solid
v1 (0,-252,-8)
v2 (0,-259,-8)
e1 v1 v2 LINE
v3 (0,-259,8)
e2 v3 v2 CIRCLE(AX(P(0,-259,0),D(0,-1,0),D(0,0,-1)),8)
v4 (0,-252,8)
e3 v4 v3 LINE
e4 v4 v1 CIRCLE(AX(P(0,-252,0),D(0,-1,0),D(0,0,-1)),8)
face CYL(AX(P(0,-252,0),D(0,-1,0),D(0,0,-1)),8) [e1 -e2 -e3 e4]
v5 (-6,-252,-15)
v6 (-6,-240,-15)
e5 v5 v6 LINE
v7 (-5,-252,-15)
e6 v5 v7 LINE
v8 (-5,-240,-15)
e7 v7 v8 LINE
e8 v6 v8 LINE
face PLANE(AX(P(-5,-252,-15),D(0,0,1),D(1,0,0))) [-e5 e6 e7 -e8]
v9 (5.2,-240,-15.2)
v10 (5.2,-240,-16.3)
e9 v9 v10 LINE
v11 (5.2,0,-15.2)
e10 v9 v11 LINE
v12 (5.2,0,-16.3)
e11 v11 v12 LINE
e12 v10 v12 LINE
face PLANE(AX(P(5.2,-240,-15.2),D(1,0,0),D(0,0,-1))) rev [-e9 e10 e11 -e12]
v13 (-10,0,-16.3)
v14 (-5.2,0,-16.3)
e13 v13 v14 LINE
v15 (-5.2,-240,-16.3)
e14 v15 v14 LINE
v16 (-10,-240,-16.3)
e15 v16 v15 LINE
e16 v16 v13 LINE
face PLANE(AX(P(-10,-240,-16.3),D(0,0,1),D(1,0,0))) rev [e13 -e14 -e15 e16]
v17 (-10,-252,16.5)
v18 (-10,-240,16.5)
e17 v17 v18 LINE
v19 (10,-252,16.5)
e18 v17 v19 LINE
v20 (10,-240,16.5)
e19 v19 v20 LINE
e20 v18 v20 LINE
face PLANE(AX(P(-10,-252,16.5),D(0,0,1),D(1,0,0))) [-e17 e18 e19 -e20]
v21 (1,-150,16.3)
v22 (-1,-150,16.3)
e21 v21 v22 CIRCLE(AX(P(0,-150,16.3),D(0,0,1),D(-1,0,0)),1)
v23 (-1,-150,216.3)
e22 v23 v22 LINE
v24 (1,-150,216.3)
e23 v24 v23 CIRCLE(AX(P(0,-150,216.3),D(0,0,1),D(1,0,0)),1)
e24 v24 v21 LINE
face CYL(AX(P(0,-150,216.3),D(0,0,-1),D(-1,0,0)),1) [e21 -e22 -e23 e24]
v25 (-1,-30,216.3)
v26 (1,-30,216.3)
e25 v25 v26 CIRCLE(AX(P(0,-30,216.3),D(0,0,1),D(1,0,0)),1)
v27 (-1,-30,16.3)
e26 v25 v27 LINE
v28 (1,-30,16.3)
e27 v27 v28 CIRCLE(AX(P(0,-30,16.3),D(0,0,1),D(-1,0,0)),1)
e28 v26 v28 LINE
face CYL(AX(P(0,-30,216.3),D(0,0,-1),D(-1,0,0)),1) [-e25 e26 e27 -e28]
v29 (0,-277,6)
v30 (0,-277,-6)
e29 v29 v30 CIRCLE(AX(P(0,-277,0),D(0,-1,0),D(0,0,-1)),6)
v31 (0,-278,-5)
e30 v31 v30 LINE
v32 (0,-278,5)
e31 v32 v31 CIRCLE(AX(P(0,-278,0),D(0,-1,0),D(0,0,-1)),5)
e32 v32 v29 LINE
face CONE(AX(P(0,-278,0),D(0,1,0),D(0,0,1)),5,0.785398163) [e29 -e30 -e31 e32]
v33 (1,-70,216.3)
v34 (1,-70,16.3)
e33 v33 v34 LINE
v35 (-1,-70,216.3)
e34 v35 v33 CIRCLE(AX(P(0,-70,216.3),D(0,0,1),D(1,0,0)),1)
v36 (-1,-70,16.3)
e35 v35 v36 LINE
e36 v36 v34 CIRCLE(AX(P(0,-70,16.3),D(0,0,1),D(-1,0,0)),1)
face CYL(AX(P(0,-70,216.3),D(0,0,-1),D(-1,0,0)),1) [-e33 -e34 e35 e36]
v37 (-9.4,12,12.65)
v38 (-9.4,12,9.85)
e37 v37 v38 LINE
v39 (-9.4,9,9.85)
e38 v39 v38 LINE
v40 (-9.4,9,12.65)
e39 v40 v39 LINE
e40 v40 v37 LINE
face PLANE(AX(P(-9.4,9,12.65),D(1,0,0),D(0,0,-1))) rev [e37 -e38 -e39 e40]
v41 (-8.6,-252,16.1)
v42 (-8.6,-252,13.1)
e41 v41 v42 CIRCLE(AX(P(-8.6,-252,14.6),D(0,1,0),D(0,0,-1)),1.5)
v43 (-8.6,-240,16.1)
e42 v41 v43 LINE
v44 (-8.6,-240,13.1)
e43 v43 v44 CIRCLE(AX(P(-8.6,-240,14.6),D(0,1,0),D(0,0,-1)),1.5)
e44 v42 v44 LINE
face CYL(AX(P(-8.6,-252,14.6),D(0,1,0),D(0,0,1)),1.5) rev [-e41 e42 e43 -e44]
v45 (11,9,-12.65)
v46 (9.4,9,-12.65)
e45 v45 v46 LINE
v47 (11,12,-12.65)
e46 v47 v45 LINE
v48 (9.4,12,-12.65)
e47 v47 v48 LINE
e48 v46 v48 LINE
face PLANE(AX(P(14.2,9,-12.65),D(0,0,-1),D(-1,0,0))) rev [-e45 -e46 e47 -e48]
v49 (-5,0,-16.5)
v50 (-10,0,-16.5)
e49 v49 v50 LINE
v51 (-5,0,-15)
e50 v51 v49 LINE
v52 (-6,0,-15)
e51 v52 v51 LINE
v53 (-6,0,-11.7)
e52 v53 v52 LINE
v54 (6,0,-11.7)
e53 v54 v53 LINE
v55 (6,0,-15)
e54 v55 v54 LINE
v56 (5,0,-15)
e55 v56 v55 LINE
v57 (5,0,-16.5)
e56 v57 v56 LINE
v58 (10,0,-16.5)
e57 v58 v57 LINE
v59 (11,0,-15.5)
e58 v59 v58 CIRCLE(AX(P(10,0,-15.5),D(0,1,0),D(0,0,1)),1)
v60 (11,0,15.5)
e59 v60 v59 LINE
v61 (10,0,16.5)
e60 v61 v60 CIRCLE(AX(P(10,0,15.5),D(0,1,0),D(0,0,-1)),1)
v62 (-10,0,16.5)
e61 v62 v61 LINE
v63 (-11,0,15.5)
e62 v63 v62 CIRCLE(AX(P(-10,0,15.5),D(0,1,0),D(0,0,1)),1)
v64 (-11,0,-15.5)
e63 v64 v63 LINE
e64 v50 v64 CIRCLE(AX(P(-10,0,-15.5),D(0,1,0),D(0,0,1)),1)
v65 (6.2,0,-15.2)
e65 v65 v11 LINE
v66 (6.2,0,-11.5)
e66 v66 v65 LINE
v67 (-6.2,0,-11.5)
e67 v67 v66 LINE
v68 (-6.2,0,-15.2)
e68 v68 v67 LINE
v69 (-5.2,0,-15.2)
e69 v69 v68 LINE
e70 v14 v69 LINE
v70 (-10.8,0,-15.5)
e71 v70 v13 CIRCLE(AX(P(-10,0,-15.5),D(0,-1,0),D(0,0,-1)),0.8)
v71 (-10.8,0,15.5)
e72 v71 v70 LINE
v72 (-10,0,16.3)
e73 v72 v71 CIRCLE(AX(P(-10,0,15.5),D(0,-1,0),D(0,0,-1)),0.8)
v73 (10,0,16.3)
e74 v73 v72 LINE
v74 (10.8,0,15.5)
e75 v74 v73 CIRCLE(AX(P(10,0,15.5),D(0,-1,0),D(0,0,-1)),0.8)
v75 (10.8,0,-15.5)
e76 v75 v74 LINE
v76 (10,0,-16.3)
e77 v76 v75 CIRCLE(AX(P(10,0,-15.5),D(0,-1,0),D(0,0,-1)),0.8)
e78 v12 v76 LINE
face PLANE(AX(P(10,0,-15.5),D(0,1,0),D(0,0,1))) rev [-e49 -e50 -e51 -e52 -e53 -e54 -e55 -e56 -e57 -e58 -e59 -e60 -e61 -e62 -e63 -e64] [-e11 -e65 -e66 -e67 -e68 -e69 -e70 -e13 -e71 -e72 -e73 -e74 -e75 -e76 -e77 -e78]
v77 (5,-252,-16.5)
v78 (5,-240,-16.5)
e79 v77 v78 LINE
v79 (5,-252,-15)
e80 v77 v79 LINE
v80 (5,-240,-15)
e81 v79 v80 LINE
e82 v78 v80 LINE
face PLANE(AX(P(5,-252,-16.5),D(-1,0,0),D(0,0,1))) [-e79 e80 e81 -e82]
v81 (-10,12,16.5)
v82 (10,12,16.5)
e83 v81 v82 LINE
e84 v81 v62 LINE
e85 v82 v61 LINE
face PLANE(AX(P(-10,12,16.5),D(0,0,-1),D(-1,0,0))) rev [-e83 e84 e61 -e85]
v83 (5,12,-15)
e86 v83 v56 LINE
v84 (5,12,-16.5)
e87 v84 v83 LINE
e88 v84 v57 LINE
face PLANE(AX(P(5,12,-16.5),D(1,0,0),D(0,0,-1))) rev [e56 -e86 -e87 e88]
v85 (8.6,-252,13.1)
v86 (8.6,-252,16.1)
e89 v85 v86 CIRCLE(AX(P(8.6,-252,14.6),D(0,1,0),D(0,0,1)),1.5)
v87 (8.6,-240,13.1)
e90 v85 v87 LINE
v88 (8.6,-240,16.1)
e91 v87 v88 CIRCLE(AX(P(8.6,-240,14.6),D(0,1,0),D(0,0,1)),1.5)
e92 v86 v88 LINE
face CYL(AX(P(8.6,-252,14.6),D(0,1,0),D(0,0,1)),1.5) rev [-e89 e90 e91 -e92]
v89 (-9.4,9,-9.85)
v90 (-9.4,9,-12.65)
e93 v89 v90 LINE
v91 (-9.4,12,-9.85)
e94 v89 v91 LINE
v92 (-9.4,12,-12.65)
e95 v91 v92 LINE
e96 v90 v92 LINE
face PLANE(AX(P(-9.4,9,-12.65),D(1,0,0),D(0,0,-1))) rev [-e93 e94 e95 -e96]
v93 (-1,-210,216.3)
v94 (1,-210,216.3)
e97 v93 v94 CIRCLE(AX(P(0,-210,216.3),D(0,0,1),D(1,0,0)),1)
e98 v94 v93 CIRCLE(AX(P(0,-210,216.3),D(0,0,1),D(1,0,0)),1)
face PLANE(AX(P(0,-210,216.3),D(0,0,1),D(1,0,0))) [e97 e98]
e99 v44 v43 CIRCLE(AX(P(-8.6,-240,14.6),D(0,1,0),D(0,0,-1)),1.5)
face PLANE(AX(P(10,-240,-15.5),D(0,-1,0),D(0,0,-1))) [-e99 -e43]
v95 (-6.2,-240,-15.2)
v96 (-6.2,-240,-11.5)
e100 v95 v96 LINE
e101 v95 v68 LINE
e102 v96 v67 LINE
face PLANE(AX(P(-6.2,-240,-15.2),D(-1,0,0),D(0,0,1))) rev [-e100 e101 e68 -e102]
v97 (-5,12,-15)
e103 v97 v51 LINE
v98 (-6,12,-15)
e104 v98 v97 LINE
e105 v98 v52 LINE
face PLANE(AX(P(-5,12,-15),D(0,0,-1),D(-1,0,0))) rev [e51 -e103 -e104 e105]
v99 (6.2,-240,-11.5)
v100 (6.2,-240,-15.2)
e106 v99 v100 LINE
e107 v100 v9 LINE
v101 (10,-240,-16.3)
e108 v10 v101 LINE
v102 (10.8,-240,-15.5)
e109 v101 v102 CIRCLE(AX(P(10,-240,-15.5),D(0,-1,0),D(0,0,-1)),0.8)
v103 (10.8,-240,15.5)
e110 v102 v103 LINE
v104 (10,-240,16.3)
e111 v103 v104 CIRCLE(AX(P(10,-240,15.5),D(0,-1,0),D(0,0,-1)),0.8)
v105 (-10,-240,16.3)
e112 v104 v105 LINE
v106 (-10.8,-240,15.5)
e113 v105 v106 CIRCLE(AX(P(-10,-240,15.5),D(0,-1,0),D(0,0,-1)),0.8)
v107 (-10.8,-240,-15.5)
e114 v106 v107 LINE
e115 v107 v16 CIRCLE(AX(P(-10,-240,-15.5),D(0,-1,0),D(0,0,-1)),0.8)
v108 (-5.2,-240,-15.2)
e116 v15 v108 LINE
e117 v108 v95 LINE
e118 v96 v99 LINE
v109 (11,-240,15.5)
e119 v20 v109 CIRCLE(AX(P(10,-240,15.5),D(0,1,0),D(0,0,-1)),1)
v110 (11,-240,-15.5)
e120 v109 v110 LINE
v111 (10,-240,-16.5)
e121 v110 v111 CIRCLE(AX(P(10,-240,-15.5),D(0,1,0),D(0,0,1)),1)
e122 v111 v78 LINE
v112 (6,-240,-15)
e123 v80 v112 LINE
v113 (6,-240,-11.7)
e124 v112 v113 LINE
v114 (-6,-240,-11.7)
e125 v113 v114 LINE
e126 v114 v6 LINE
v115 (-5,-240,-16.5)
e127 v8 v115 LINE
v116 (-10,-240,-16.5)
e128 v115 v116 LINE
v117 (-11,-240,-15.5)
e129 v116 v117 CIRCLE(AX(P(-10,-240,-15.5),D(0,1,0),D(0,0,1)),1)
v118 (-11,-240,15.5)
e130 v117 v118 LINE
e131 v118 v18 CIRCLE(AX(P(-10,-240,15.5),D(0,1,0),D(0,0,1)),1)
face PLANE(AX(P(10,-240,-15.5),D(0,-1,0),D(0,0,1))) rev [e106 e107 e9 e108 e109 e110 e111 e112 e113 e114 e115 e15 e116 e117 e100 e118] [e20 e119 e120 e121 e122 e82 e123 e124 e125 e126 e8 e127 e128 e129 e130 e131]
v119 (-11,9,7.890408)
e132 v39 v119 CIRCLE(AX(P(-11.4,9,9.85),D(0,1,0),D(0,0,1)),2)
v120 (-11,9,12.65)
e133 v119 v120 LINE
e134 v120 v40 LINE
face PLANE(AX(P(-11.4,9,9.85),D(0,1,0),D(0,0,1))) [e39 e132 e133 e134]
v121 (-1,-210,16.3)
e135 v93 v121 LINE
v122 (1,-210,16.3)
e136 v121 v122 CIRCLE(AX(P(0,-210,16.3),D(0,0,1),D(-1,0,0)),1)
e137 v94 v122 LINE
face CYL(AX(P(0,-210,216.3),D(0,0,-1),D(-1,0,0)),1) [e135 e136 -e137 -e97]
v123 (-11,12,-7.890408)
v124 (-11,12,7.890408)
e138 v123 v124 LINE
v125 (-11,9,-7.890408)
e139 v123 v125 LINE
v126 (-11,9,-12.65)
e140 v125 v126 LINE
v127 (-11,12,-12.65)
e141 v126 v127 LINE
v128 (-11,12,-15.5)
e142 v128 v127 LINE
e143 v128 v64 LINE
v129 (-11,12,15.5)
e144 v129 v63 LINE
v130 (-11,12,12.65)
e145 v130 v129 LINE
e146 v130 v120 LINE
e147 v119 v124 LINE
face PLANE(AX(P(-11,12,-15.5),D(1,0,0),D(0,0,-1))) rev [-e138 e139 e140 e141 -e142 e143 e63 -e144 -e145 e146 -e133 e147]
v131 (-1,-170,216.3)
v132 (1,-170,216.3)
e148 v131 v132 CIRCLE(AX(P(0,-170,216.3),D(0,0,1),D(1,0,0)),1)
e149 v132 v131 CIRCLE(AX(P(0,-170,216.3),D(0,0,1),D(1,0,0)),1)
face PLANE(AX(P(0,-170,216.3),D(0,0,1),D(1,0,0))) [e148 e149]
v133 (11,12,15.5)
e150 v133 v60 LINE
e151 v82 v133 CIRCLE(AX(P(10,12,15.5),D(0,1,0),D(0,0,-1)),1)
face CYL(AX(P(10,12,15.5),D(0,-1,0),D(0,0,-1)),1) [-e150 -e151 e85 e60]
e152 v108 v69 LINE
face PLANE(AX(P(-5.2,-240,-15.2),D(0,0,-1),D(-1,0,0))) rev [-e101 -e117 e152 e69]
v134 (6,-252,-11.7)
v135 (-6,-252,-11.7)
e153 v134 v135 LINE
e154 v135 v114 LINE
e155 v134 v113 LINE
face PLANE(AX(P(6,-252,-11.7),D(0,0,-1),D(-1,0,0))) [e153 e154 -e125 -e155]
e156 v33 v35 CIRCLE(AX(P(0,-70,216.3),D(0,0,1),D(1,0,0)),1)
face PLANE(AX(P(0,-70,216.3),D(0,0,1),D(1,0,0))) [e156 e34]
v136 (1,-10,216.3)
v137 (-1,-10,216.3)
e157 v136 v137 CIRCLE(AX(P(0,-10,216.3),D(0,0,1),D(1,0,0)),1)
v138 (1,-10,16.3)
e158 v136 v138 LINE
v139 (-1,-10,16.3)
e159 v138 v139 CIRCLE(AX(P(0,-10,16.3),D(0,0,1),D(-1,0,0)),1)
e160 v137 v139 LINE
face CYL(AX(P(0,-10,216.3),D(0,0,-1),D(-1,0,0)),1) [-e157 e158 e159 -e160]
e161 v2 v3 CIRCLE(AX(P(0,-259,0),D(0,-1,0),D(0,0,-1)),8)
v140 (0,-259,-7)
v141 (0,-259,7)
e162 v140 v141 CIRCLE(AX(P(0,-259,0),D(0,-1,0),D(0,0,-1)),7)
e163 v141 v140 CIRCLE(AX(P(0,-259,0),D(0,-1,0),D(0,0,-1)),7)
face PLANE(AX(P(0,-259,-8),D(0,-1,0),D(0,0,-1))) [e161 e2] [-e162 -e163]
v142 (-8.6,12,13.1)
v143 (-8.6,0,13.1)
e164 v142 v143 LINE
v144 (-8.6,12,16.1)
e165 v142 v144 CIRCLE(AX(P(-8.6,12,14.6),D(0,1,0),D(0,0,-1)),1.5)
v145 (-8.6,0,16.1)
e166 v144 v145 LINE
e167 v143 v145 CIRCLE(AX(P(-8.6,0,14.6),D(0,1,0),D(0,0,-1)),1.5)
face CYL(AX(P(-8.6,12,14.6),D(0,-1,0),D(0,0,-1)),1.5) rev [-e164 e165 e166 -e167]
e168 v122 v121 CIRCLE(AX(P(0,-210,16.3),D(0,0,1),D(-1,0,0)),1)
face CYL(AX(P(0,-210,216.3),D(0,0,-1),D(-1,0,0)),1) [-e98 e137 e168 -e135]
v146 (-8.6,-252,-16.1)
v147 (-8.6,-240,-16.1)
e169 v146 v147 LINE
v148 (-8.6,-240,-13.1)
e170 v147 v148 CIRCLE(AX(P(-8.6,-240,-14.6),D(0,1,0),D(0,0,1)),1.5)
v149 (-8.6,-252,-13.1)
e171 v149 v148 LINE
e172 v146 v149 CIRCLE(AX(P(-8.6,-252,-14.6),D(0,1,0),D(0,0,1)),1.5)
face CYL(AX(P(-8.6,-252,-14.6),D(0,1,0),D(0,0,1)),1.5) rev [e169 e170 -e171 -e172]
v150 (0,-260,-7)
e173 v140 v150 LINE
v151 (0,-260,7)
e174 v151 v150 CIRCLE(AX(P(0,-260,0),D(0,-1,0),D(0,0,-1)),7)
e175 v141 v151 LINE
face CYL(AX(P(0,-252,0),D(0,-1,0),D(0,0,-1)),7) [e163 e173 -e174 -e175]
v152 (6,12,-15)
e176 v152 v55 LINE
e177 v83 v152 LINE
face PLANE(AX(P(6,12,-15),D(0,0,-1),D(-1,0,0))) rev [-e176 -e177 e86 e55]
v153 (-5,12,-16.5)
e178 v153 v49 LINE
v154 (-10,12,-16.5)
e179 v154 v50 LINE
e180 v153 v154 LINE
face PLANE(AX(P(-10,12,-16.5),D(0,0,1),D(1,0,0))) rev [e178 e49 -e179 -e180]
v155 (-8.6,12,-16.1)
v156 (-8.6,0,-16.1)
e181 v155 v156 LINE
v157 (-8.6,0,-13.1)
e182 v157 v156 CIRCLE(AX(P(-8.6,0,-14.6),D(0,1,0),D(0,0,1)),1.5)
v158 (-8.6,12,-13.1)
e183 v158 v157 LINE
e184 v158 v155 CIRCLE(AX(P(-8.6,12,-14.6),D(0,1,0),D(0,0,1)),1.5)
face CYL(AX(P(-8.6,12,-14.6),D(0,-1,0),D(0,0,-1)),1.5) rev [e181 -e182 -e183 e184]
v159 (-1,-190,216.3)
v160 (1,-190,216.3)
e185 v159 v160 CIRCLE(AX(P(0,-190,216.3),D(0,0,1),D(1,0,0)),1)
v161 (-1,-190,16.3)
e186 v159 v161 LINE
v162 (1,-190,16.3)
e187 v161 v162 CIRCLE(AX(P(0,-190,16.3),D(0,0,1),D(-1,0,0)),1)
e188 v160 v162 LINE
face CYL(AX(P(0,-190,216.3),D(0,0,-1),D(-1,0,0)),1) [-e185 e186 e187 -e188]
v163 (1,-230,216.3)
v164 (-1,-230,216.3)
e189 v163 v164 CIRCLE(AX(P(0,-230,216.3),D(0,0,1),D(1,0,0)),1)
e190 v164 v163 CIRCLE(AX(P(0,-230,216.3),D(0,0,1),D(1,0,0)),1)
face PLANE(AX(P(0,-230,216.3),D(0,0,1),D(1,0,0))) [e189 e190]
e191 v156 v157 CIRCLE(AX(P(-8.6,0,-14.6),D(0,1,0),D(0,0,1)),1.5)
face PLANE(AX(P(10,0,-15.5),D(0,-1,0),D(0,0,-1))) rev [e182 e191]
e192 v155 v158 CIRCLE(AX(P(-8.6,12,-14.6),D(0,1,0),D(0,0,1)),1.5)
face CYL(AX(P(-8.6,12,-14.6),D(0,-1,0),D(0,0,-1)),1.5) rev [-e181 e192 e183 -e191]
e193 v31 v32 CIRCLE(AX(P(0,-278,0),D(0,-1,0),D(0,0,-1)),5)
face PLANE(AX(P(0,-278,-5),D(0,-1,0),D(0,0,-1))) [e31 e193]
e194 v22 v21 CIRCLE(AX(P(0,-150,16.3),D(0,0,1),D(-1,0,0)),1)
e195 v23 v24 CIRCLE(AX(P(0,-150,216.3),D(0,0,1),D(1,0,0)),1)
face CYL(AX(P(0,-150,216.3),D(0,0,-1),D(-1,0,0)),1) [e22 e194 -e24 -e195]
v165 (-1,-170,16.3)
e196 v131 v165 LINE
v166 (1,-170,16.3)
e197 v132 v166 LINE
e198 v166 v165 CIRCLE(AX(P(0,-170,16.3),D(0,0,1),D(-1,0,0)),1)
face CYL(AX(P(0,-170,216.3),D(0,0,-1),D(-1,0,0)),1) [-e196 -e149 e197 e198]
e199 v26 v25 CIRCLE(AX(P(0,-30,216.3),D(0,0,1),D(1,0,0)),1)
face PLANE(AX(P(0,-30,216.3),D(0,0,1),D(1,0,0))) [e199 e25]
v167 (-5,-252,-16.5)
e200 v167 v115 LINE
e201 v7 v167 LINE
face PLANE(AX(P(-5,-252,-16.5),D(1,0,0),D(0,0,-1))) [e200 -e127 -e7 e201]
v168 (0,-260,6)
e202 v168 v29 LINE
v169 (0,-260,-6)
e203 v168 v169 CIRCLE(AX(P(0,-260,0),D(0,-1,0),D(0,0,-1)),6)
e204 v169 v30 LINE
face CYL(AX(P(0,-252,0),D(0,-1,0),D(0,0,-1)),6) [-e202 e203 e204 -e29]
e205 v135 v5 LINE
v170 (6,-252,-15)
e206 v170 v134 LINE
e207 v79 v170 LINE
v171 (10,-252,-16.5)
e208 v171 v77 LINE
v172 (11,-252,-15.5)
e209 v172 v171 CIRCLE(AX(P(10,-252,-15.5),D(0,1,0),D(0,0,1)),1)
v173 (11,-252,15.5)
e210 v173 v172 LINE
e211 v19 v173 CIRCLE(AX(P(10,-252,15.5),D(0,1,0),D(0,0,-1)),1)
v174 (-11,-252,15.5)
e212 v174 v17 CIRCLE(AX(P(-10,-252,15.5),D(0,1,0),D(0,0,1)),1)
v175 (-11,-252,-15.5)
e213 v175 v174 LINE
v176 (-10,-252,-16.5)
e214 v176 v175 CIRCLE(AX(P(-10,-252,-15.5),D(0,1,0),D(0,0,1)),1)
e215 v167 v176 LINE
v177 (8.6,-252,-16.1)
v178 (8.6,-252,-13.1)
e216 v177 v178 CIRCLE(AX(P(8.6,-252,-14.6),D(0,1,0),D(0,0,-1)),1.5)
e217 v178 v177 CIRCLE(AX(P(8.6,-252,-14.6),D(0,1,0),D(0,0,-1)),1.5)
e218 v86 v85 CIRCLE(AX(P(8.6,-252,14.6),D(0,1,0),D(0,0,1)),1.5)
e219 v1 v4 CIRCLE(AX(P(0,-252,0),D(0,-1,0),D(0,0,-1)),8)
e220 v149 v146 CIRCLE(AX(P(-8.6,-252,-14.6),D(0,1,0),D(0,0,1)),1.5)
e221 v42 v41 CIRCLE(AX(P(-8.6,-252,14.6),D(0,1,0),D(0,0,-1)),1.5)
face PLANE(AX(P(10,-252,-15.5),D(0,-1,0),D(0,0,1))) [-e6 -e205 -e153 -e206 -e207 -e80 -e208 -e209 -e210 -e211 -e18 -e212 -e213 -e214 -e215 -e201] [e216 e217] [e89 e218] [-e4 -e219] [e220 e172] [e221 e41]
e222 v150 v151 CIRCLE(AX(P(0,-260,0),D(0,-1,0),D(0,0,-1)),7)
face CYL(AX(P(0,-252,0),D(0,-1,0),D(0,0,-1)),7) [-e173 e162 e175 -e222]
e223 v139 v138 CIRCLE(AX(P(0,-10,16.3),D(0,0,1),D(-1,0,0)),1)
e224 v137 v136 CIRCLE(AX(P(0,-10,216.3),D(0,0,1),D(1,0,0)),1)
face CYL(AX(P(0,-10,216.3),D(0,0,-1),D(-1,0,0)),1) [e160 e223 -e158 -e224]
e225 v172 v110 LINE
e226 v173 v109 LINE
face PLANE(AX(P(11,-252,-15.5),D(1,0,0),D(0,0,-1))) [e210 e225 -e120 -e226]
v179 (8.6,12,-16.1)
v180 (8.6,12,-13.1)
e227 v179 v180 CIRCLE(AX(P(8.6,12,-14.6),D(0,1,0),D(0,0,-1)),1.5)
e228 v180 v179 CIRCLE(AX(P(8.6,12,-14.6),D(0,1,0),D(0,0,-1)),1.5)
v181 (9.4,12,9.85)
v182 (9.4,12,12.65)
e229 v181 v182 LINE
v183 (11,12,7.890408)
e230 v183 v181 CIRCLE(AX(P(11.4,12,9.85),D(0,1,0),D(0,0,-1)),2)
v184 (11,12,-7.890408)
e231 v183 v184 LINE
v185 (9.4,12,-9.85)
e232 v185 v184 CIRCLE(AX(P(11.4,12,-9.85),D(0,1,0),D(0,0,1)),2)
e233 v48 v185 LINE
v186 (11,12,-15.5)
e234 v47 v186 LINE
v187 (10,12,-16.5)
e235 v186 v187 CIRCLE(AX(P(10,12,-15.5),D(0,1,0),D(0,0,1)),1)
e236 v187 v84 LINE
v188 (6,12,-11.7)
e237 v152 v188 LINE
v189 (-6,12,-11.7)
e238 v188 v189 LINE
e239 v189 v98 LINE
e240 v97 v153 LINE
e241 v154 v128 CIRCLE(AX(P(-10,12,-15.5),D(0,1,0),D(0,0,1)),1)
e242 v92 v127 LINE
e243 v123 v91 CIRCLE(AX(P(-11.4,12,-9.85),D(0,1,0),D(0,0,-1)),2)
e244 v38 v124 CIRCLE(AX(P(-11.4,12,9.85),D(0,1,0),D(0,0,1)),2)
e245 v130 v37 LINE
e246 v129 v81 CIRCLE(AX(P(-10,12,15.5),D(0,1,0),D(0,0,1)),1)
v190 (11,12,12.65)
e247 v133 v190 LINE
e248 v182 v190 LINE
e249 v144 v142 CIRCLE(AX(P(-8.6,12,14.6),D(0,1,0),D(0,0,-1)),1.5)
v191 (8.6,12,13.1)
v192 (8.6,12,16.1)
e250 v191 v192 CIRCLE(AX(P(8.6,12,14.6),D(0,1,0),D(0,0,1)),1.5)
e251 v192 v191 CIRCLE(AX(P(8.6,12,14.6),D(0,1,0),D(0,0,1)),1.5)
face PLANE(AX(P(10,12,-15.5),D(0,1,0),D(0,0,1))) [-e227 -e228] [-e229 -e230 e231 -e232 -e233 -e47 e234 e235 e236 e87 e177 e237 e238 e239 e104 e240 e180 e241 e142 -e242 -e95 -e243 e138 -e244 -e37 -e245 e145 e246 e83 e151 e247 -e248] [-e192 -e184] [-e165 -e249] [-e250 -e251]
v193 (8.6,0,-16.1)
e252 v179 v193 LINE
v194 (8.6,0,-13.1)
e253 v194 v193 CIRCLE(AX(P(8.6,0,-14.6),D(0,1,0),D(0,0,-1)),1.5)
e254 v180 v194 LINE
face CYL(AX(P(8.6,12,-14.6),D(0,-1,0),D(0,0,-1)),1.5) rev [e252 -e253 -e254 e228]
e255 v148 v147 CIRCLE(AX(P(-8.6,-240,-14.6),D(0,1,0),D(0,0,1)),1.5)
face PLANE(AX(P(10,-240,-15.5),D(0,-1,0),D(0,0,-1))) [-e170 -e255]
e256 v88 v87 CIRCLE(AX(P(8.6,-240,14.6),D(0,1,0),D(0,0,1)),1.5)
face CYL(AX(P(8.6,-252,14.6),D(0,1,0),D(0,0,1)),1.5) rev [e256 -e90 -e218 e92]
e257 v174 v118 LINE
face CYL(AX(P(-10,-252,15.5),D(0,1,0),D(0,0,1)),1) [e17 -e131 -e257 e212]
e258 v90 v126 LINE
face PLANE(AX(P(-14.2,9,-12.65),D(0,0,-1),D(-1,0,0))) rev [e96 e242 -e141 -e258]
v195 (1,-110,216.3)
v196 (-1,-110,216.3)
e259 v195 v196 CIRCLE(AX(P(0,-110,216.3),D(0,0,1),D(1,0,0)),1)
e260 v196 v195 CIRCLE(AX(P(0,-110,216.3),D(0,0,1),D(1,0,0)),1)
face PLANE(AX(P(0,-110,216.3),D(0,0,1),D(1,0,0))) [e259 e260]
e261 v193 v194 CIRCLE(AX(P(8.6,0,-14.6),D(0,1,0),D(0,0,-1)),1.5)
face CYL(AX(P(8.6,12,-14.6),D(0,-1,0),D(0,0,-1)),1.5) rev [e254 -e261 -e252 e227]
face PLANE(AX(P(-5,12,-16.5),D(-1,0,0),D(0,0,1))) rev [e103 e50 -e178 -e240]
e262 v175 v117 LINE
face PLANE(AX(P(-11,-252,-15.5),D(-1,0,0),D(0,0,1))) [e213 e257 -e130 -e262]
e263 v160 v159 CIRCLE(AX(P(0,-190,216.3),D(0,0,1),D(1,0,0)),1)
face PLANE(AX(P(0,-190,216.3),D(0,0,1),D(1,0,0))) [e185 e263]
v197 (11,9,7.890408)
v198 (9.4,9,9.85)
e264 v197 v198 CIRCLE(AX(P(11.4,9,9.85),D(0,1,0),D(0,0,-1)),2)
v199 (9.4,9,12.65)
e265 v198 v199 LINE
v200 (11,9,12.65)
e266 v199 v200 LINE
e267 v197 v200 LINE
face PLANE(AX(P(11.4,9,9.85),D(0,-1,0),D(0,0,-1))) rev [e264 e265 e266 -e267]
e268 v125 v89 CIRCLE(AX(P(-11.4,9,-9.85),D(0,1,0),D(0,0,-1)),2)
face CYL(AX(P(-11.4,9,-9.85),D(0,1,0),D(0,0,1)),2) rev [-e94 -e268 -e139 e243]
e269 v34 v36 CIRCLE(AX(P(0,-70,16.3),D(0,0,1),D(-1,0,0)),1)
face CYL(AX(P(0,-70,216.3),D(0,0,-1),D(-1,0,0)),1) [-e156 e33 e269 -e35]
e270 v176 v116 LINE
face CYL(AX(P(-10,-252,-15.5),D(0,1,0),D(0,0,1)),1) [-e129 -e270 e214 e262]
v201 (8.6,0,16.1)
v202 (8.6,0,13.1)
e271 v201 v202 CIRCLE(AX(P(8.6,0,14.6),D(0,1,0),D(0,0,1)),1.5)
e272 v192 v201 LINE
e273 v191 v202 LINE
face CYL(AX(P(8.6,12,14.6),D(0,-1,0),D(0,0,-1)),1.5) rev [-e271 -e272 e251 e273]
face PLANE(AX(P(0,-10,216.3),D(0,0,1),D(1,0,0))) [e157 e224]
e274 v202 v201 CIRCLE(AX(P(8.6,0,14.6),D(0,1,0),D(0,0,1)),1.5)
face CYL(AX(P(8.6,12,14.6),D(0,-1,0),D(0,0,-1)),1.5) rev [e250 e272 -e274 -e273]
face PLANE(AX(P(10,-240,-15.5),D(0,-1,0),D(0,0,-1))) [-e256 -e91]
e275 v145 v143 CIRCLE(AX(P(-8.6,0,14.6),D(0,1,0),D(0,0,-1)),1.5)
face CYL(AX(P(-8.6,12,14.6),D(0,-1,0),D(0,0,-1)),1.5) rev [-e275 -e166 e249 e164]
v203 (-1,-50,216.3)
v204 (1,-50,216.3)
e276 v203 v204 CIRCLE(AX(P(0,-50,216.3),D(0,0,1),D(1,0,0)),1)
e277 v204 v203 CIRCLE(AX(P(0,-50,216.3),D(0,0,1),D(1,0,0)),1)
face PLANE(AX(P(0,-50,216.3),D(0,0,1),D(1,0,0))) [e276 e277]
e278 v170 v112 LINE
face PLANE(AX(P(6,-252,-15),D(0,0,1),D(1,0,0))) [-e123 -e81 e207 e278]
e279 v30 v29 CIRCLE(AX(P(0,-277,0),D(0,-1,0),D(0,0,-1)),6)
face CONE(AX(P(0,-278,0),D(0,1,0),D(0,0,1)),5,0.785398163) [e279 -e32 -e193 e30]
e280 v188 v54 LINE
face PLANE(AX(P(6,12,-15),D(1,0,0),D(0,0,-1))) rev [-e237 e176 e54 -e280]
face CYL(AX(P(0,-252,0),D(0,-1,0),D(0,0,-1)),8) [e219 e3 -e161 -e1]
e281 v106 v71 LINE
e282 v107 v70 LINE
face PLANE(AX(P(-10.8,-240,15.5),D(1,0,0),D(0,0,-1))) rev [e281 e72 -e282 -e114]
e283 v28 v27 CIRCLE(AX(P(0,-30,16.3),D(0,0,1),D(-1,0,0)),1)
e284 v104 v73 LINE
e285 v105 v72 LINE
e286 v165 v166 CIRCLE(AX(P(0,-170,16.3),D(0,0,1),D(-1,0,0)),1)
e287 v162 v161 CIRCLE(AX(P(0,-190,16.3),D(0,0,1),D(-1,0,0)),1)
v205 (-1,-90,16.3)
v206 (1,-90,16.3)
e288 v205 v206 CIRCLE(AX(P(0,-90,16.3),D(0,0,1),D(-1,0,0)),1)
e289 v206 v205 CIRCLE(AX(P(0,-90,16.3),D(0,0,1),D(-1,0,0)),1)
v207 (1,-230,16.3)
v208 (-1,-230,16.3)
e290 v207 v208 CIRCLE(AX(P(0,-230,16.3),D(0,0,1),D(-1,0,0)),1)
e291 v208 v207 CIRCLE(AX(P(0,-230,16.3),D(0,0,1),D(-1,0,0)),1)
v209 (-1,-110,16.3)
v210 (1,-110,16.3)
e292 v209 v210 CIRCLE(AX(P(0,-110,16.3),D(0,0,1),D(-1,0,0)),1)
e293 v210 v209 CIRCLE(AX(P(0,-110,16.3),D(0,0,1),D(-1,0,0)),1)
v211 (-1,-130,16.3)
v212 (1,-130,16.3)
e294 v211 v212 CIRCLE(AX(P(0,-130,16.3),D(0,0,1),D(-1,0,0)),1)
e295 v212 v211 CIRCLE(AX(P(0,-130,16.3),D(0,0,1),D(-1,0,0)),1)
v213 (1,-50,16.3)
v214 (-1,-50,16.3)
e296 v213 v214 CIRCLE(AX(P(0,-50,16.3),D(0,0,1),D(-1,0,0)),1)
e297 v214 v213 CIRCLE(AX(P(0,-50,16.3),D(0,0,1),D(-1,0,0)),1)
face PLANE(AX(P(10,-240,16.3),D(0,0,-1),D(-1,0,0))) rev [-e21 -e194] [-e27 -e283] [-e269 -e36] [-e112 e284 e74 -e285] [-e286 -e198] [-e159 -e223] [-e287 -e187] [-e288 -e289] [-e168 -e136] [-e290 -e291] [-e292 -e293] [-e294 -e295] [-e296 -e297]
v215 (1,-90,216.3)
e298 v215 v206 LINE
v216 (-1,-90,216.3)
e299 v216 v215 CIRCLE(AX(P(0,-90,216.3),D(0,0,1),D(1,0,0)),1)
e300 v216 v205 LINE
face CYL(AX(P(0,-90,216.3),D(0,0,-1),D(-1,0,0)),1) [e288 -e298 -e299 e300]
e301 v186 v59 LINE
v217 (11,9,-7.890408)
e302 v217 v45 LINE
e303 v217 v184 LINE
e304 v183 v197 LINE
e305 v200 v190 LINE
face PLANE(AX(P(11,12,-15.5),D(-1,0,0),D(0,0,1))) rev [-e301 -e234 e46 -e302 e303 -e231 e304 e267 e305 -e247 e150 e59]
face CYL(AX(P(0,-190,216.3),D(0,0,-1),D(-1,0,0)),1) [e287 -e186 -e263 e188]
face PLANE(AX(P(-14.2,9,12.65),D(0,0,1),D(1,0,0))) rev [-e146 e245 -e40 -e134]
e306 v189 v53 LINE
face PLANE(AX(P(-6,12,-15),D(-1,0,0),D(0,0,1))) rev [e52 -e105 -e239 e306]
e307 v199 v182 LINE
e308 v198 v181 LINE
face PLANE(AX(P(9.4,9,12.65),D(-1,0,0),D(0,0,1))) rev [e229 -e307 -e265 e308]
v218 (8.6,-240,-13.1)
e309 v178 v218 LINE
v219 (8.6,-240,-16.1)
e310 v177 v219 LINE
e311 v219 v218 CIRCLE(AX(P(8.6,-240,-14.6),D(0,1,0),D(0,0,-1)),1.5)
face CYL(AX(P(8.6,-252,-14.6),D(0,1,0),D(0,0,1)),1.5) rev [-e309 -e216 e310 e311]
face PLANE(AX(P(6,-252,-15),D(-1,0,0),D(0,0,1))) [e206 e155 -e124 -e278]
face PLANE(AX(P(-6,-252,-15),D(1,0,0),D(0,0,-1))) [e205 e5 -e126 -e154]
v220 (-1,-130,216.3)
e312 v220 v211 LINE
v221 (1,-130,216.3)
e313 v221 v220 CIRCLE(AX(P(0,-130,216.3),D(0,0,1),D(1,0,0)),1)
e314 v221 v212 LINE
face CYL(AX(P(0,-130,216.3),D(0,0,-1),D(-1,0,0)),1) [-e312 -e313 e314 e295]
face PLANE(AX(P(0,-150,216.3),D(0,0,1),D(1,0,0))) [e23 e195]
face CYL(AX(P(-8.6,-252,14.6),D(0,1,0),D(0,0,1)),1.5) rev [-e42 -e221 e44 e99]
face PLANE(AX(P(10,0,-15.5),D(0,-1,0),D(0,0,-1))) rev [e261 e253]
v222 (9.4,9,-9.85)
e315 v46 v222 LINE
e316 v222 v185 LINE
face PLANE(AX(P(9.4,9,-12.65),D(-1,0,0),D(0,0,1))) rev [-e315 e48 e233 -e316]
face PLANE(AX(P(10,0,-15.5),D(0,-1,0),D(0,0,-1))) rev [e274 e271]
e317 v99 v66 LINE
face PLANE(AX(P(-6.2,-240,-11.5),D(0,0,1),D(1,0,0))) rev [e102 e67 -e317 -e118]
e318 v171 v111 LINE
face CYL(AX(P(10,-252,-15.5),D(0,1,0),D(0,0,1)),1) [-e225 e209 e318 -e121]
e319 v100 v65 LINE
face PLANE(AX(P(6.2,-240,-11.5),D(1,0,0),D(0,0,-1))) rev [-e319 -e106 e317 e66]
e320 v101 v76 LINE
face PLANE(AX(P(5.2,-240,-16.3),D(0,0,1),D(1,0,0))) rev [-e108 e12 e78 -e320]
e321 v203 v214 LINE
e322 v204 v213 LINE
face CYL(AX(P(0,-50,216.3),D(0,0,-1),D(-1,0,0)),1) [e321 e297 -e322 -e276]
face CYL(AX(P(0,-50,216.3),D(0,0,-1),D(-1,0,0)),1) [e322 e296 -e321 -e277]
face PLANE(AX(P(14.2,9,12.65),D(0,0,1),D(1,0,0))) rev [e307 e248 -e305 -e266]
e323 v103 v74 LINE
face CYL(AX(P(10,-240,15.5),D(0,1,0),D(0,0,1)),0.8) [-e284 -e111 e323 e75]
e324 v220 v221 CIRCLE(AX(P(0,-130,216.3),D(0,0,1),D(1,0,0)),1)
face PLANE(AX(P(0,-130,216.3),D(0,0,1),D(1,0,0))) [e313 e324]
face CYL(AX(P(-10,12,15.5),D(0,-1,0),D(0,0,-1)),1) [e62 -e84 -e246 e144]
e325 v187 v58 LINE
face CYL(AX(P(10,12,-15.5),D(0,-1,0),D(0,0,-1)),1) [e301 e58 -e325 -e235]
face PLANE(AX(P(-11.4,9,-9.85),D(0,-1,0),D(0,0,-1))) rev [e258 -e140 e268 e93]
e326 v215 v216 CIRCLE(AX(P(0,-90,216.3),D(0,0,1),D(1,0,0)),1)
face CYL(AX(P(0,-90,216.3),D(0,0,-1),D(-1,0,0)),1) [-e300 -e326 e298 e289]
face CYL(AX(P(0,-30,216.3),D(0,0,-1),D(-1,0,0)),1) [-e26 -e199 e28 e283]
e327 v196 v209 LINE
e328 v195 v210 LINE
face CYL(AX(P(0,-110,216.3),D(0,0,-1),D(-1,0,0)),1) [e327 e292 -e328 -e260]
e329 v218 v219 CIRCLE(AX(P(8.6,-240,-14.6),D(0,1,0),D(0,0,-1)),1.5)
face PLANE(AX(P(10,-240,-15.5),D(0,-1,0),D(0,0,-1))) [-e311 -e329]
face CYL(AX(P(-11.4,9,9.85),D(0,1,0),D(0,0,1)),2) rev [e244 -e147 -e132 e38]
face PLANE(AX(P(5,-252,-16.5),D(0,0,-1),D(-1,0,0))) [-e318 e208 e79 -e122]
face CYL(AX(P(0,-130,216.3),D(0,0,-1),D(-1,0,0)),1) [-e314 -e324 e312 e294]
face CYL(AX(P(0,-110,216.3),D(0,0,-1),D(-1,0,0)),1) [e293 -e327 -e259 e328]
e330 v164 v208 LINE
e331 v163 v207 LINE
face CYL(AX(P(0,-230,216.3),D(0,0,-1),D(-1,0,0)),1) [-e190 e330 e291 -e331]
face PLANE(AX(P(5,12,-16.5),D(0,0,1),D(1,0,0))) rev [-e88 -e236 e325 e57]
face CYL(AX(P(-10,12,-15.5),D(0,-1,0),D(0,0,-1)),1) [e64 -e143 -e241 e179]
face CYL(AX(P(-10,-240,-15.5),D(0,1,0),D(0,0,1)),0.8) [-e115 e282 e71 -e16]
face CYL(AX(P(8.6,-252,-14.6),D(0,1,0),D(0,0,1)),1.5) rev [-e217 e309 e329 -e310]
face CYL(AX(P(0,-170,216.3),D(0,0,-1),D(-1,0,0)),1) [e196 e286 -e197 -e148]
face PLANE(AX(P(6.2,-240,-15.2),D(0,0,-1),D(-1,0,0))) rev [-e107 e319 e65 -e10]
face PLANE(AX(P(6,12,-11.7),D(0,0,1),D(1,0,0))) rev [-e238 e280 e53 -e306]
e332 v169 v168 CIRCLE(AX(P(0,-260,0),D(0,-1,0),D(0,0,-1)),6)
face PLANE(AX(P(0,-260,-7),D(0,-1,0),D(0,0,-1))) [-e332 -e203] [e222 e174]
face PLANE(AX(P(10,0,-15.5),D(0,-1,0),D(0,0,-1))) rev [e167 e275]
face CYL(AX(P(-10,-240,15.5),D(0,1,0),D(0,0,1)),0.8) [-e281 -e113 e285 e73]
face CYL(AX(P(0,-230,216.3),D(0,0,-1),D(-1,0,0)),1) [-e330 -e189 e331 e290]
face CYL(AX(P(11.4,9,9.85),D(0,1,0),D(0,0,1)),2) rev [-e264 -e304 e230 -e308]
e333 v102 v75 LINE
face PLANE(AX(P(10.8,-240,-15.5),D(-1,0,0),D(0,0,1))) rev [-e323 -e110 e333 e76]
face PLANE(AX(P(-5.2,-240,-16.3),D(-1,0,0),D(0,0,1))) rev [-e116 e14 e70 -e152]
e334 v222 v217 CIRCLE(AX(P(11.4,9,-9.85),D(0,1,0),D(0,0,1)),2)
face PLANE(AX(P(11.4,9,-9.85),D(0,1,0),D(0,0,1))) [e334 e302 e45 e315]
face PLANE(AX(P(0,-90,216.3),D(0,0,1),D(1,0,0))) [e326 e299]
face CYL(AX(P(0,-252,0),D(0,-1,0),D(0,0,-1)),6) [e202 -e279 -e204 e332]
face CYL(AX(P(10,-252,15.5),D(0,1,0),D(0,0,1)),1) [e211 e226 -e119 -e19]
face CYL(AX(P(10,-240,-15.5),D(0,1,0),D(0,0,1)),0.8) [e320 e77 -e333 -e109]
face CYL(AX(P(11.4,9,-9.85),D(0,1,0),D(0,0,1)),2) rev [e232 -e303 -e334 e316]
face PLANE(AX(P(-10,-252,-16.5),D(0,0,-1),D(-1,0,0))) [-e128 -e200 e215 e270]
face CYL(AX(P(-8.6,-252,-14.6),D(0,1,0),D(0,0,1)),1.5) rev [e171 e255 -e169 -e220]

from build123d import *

# Parameters (mm, degrees)
SKETCH_1_R             = 1.5
EXTRUDE_1_DEPTH        = 12
CUT_EXTRUDE_2_DEPTH    = 3
EXTRUDE_3_DEPTH        = 240
SKETCH_5_R             = 1
EXTRUDE_4_DEPTH        = 200
PATTERN_LINEAR_1_COUNT = 12
PATTERN_LINEAR_1_PITCH = 20


with BuildPart() as part:
    # 草圖1 → 伸長1 (new body)
    with BuildSketch(Plane(origin=(0, 0, 0), x_dir=(1, 0, 0), z_dir=(0, 1, 0))):
        with BuildLine():
            Line((-10, 16.5), (-5, 16.5))
            Line((-5, 16.5), (-5, 15))
            Line((-5, 15), (-6, 15))
            Line((-6, 15), (-6, 11.7))
            Line((-6, 11.7), (6, 11.7))
            Line((6, 11.7), (6, 15))
            Line((6, 15), (5, 15))
            Line((5, 15), (5, 16.5))
            Line((5, 16.5), (10, 16.5))
            ThreePointArc((10, 16.5), (10.707106781, 16.207106781), (11, 15.5))
            Line((11, 15.5), (11, -15.5))
            ThreePointArc((11, -15.5), (10.707106781, -16.207106781), (10, -16.5))
            Line((10, -16.5), (-10, -16.5))
            ThreePointArc((-10, -16.5), (-10.707106781, -16.207106781), (-11, -15.5))
            Line((-11, -15.5), (-11, 15.5))
            ThreePointArc((-11, 15.5), (-10.707106781, 16.207106781), (-10, 16.5))
        make_face()
        with Locations(Location((-8.6, 14.6, 0), (0, 0, 270))):
            Circle(SKETCH_1_R, mode=Mode.SUBTRACT)
        with Locations(Location((8.6, 14.6, 0), (0, 0, 90))):
            Circle(SKETCH_1_R, mode=Mode.SUBTRACT)
        with Locations(Location((8.6, -14.6, 0), (0, 0, 270))):
            Circle(SKETCH_1_R, mode=Mode.SUBTRACT)
        with Locations(Location((-8.6, -14.6, 0), (0, 0, 90))):
            Circle(SKETCH_1_R, mode=Mode.SUBTRACT)
    extrude_1 = extrude(amount=EXTRUDE_1_DEPTH)

    # 草圖2 → 伸長2 (cut)
    with BuildSketch(Plane(origin=(0, 12, 0), x_dir=(1, 0, 0), z_dir=(0, 1, 0))):
        with BuildLine():
            Line((-14.2, 12.65), (-9.4, 12.65))
            Line((-9.4, 12.65), (-9.4, 9.85))
            ThreePointArc((-9.4, 9.85), (-9.985786438, 8.435786438), (-11.4, 7.85))
            Line((-11.4, 7.85), (-14.2, 7.85))
            Line((-14.2, 7.85), (-14.2, 12.65))
        make_face()
        with BuildLine():
            Line((9.4, 12.65), (9.4, 9.85))
            ThreePointArc((9.4, 9.85), (9.985786438, 8.435786438), (11.4, 7.85))
            Line((11.4, 7.85), (14.2, 7.85))
            Line((14.2, 7.85), (14.2, 12.65))
            Line((14.2, 12.65), (9.4, 12.65))
        make_face()
        with BuildLine():
            Line((14.2, -12.65), (9.4, -12.65))
            Line((9.4, -12.65), (9.4, -9.85))
            ThreePointArc((9.4, -9.85), (9.985786438, -8.435786438), (11.4, -7.85))
            Line((11.4, -7.85), (14.2, -7.85))
            Line((14.2, -7.85), (14.2, -12.65))
        make_face()
        with BuildLine():
            Line((-9.4, -12.65), (-9.4, -9.85))
            ThreePointArc((-9.4, -9.85), (-9.985786438, -8.435786438), (-11.4, -7.85))
            Line((-11.4, -7.85), (-14.2, -7.85))
            Line((-14.2, -7.85), (-14.2, -12.65))
            Line((-14.2, -12.65), (-9.4, -12.65))
        make_face()
    extrude(amount=-CUT_EXTRUDE_2_DEPTH, mode=Mode.SUBTRACT)

    # 草圖3 → 伸長3 (add)
    with BuildSketch(Plane.XZ):
        with BuildLine():
            Line((-5.2, -16.3), (-5.2, -15.2))
            Line((-5.2, -15.2), (-6.2, -15.2))
            Line((-6.2, -15.2), (-6.2, -11.5))
            Line((-6.2, -11.5), (6.2, -11.5))
            Line((6.2, -11.5), (6.2, -15.2))
            Line((6.2, -15.2), (5.2, -15.2))
            Line((5.2, -15.2), (5.2, -16.3))
            Line((5.2, -16.3), (10, -16.3))
            ThreePointArc((10, -16.3), (10.565685425, -16.065685425), (10.8, -15.5))
            Line((10.8, -15.5), (10.8, 15.5))
            ThreePointArc((10.8, 15.5), (10.565685425, 16.065685425), (10, 16.3))
            Line((10, 16.3), (-10, 16.3))
            ThreePointArc((-10, 16.3), (-10.565685425, 16.065685425), (-10.8, 15.5))
            Line((-10.8, 15.5), (-10.8, -15.5))
            ThreePointArc((-10.8, -15.5), (-10.565685425, -16.065685425), (-10, -16.3))
            Line((-10, -16.3), (-5.2, -16.3))
        make_face()
    extrude(amount=EXTRUDE_3_DEPTH)

    # 鏡射1: 伸長1 across plane
    add(extrude_1.mirror(Plane.ZX.offset(-120)))

    # 草圖4 → 旋轉1 (revolve)
    with BuildSketch(Plane(origin=(0, 0, 0), x_dir=(0, 0, -1), z_dir=(1, 0, 0))):
        Polygon((8, -252), (8, -259), (7, -259), (7, -260), (6, -260), (6, -277), (5, -278), (0, -278), (0, -252), align=None)
    revolve(axis=Axis((0, -252, 0), (0, 1, 0)))

    # 草圖5 → 伸長4 (add)
    with BuildSketch(Plane.XY.offset(16.3)):
        with Locations(Location((0, -10, 0), (0, 0, 180))):
            Circle(SKETCH_5_R)
    extrude_4 = extrude(amount=EXTRUDE_4_DEPTH)

    # 阵列(线性)1: 伸長4 ×12
    with Locations(*[(0, -i * PATTERN_LINEAR_1_PITCH, 0) for i in range(1, PATTERN_LINEAR_1_COUNT)]):
        add(extrude_4)


solid = part.part
